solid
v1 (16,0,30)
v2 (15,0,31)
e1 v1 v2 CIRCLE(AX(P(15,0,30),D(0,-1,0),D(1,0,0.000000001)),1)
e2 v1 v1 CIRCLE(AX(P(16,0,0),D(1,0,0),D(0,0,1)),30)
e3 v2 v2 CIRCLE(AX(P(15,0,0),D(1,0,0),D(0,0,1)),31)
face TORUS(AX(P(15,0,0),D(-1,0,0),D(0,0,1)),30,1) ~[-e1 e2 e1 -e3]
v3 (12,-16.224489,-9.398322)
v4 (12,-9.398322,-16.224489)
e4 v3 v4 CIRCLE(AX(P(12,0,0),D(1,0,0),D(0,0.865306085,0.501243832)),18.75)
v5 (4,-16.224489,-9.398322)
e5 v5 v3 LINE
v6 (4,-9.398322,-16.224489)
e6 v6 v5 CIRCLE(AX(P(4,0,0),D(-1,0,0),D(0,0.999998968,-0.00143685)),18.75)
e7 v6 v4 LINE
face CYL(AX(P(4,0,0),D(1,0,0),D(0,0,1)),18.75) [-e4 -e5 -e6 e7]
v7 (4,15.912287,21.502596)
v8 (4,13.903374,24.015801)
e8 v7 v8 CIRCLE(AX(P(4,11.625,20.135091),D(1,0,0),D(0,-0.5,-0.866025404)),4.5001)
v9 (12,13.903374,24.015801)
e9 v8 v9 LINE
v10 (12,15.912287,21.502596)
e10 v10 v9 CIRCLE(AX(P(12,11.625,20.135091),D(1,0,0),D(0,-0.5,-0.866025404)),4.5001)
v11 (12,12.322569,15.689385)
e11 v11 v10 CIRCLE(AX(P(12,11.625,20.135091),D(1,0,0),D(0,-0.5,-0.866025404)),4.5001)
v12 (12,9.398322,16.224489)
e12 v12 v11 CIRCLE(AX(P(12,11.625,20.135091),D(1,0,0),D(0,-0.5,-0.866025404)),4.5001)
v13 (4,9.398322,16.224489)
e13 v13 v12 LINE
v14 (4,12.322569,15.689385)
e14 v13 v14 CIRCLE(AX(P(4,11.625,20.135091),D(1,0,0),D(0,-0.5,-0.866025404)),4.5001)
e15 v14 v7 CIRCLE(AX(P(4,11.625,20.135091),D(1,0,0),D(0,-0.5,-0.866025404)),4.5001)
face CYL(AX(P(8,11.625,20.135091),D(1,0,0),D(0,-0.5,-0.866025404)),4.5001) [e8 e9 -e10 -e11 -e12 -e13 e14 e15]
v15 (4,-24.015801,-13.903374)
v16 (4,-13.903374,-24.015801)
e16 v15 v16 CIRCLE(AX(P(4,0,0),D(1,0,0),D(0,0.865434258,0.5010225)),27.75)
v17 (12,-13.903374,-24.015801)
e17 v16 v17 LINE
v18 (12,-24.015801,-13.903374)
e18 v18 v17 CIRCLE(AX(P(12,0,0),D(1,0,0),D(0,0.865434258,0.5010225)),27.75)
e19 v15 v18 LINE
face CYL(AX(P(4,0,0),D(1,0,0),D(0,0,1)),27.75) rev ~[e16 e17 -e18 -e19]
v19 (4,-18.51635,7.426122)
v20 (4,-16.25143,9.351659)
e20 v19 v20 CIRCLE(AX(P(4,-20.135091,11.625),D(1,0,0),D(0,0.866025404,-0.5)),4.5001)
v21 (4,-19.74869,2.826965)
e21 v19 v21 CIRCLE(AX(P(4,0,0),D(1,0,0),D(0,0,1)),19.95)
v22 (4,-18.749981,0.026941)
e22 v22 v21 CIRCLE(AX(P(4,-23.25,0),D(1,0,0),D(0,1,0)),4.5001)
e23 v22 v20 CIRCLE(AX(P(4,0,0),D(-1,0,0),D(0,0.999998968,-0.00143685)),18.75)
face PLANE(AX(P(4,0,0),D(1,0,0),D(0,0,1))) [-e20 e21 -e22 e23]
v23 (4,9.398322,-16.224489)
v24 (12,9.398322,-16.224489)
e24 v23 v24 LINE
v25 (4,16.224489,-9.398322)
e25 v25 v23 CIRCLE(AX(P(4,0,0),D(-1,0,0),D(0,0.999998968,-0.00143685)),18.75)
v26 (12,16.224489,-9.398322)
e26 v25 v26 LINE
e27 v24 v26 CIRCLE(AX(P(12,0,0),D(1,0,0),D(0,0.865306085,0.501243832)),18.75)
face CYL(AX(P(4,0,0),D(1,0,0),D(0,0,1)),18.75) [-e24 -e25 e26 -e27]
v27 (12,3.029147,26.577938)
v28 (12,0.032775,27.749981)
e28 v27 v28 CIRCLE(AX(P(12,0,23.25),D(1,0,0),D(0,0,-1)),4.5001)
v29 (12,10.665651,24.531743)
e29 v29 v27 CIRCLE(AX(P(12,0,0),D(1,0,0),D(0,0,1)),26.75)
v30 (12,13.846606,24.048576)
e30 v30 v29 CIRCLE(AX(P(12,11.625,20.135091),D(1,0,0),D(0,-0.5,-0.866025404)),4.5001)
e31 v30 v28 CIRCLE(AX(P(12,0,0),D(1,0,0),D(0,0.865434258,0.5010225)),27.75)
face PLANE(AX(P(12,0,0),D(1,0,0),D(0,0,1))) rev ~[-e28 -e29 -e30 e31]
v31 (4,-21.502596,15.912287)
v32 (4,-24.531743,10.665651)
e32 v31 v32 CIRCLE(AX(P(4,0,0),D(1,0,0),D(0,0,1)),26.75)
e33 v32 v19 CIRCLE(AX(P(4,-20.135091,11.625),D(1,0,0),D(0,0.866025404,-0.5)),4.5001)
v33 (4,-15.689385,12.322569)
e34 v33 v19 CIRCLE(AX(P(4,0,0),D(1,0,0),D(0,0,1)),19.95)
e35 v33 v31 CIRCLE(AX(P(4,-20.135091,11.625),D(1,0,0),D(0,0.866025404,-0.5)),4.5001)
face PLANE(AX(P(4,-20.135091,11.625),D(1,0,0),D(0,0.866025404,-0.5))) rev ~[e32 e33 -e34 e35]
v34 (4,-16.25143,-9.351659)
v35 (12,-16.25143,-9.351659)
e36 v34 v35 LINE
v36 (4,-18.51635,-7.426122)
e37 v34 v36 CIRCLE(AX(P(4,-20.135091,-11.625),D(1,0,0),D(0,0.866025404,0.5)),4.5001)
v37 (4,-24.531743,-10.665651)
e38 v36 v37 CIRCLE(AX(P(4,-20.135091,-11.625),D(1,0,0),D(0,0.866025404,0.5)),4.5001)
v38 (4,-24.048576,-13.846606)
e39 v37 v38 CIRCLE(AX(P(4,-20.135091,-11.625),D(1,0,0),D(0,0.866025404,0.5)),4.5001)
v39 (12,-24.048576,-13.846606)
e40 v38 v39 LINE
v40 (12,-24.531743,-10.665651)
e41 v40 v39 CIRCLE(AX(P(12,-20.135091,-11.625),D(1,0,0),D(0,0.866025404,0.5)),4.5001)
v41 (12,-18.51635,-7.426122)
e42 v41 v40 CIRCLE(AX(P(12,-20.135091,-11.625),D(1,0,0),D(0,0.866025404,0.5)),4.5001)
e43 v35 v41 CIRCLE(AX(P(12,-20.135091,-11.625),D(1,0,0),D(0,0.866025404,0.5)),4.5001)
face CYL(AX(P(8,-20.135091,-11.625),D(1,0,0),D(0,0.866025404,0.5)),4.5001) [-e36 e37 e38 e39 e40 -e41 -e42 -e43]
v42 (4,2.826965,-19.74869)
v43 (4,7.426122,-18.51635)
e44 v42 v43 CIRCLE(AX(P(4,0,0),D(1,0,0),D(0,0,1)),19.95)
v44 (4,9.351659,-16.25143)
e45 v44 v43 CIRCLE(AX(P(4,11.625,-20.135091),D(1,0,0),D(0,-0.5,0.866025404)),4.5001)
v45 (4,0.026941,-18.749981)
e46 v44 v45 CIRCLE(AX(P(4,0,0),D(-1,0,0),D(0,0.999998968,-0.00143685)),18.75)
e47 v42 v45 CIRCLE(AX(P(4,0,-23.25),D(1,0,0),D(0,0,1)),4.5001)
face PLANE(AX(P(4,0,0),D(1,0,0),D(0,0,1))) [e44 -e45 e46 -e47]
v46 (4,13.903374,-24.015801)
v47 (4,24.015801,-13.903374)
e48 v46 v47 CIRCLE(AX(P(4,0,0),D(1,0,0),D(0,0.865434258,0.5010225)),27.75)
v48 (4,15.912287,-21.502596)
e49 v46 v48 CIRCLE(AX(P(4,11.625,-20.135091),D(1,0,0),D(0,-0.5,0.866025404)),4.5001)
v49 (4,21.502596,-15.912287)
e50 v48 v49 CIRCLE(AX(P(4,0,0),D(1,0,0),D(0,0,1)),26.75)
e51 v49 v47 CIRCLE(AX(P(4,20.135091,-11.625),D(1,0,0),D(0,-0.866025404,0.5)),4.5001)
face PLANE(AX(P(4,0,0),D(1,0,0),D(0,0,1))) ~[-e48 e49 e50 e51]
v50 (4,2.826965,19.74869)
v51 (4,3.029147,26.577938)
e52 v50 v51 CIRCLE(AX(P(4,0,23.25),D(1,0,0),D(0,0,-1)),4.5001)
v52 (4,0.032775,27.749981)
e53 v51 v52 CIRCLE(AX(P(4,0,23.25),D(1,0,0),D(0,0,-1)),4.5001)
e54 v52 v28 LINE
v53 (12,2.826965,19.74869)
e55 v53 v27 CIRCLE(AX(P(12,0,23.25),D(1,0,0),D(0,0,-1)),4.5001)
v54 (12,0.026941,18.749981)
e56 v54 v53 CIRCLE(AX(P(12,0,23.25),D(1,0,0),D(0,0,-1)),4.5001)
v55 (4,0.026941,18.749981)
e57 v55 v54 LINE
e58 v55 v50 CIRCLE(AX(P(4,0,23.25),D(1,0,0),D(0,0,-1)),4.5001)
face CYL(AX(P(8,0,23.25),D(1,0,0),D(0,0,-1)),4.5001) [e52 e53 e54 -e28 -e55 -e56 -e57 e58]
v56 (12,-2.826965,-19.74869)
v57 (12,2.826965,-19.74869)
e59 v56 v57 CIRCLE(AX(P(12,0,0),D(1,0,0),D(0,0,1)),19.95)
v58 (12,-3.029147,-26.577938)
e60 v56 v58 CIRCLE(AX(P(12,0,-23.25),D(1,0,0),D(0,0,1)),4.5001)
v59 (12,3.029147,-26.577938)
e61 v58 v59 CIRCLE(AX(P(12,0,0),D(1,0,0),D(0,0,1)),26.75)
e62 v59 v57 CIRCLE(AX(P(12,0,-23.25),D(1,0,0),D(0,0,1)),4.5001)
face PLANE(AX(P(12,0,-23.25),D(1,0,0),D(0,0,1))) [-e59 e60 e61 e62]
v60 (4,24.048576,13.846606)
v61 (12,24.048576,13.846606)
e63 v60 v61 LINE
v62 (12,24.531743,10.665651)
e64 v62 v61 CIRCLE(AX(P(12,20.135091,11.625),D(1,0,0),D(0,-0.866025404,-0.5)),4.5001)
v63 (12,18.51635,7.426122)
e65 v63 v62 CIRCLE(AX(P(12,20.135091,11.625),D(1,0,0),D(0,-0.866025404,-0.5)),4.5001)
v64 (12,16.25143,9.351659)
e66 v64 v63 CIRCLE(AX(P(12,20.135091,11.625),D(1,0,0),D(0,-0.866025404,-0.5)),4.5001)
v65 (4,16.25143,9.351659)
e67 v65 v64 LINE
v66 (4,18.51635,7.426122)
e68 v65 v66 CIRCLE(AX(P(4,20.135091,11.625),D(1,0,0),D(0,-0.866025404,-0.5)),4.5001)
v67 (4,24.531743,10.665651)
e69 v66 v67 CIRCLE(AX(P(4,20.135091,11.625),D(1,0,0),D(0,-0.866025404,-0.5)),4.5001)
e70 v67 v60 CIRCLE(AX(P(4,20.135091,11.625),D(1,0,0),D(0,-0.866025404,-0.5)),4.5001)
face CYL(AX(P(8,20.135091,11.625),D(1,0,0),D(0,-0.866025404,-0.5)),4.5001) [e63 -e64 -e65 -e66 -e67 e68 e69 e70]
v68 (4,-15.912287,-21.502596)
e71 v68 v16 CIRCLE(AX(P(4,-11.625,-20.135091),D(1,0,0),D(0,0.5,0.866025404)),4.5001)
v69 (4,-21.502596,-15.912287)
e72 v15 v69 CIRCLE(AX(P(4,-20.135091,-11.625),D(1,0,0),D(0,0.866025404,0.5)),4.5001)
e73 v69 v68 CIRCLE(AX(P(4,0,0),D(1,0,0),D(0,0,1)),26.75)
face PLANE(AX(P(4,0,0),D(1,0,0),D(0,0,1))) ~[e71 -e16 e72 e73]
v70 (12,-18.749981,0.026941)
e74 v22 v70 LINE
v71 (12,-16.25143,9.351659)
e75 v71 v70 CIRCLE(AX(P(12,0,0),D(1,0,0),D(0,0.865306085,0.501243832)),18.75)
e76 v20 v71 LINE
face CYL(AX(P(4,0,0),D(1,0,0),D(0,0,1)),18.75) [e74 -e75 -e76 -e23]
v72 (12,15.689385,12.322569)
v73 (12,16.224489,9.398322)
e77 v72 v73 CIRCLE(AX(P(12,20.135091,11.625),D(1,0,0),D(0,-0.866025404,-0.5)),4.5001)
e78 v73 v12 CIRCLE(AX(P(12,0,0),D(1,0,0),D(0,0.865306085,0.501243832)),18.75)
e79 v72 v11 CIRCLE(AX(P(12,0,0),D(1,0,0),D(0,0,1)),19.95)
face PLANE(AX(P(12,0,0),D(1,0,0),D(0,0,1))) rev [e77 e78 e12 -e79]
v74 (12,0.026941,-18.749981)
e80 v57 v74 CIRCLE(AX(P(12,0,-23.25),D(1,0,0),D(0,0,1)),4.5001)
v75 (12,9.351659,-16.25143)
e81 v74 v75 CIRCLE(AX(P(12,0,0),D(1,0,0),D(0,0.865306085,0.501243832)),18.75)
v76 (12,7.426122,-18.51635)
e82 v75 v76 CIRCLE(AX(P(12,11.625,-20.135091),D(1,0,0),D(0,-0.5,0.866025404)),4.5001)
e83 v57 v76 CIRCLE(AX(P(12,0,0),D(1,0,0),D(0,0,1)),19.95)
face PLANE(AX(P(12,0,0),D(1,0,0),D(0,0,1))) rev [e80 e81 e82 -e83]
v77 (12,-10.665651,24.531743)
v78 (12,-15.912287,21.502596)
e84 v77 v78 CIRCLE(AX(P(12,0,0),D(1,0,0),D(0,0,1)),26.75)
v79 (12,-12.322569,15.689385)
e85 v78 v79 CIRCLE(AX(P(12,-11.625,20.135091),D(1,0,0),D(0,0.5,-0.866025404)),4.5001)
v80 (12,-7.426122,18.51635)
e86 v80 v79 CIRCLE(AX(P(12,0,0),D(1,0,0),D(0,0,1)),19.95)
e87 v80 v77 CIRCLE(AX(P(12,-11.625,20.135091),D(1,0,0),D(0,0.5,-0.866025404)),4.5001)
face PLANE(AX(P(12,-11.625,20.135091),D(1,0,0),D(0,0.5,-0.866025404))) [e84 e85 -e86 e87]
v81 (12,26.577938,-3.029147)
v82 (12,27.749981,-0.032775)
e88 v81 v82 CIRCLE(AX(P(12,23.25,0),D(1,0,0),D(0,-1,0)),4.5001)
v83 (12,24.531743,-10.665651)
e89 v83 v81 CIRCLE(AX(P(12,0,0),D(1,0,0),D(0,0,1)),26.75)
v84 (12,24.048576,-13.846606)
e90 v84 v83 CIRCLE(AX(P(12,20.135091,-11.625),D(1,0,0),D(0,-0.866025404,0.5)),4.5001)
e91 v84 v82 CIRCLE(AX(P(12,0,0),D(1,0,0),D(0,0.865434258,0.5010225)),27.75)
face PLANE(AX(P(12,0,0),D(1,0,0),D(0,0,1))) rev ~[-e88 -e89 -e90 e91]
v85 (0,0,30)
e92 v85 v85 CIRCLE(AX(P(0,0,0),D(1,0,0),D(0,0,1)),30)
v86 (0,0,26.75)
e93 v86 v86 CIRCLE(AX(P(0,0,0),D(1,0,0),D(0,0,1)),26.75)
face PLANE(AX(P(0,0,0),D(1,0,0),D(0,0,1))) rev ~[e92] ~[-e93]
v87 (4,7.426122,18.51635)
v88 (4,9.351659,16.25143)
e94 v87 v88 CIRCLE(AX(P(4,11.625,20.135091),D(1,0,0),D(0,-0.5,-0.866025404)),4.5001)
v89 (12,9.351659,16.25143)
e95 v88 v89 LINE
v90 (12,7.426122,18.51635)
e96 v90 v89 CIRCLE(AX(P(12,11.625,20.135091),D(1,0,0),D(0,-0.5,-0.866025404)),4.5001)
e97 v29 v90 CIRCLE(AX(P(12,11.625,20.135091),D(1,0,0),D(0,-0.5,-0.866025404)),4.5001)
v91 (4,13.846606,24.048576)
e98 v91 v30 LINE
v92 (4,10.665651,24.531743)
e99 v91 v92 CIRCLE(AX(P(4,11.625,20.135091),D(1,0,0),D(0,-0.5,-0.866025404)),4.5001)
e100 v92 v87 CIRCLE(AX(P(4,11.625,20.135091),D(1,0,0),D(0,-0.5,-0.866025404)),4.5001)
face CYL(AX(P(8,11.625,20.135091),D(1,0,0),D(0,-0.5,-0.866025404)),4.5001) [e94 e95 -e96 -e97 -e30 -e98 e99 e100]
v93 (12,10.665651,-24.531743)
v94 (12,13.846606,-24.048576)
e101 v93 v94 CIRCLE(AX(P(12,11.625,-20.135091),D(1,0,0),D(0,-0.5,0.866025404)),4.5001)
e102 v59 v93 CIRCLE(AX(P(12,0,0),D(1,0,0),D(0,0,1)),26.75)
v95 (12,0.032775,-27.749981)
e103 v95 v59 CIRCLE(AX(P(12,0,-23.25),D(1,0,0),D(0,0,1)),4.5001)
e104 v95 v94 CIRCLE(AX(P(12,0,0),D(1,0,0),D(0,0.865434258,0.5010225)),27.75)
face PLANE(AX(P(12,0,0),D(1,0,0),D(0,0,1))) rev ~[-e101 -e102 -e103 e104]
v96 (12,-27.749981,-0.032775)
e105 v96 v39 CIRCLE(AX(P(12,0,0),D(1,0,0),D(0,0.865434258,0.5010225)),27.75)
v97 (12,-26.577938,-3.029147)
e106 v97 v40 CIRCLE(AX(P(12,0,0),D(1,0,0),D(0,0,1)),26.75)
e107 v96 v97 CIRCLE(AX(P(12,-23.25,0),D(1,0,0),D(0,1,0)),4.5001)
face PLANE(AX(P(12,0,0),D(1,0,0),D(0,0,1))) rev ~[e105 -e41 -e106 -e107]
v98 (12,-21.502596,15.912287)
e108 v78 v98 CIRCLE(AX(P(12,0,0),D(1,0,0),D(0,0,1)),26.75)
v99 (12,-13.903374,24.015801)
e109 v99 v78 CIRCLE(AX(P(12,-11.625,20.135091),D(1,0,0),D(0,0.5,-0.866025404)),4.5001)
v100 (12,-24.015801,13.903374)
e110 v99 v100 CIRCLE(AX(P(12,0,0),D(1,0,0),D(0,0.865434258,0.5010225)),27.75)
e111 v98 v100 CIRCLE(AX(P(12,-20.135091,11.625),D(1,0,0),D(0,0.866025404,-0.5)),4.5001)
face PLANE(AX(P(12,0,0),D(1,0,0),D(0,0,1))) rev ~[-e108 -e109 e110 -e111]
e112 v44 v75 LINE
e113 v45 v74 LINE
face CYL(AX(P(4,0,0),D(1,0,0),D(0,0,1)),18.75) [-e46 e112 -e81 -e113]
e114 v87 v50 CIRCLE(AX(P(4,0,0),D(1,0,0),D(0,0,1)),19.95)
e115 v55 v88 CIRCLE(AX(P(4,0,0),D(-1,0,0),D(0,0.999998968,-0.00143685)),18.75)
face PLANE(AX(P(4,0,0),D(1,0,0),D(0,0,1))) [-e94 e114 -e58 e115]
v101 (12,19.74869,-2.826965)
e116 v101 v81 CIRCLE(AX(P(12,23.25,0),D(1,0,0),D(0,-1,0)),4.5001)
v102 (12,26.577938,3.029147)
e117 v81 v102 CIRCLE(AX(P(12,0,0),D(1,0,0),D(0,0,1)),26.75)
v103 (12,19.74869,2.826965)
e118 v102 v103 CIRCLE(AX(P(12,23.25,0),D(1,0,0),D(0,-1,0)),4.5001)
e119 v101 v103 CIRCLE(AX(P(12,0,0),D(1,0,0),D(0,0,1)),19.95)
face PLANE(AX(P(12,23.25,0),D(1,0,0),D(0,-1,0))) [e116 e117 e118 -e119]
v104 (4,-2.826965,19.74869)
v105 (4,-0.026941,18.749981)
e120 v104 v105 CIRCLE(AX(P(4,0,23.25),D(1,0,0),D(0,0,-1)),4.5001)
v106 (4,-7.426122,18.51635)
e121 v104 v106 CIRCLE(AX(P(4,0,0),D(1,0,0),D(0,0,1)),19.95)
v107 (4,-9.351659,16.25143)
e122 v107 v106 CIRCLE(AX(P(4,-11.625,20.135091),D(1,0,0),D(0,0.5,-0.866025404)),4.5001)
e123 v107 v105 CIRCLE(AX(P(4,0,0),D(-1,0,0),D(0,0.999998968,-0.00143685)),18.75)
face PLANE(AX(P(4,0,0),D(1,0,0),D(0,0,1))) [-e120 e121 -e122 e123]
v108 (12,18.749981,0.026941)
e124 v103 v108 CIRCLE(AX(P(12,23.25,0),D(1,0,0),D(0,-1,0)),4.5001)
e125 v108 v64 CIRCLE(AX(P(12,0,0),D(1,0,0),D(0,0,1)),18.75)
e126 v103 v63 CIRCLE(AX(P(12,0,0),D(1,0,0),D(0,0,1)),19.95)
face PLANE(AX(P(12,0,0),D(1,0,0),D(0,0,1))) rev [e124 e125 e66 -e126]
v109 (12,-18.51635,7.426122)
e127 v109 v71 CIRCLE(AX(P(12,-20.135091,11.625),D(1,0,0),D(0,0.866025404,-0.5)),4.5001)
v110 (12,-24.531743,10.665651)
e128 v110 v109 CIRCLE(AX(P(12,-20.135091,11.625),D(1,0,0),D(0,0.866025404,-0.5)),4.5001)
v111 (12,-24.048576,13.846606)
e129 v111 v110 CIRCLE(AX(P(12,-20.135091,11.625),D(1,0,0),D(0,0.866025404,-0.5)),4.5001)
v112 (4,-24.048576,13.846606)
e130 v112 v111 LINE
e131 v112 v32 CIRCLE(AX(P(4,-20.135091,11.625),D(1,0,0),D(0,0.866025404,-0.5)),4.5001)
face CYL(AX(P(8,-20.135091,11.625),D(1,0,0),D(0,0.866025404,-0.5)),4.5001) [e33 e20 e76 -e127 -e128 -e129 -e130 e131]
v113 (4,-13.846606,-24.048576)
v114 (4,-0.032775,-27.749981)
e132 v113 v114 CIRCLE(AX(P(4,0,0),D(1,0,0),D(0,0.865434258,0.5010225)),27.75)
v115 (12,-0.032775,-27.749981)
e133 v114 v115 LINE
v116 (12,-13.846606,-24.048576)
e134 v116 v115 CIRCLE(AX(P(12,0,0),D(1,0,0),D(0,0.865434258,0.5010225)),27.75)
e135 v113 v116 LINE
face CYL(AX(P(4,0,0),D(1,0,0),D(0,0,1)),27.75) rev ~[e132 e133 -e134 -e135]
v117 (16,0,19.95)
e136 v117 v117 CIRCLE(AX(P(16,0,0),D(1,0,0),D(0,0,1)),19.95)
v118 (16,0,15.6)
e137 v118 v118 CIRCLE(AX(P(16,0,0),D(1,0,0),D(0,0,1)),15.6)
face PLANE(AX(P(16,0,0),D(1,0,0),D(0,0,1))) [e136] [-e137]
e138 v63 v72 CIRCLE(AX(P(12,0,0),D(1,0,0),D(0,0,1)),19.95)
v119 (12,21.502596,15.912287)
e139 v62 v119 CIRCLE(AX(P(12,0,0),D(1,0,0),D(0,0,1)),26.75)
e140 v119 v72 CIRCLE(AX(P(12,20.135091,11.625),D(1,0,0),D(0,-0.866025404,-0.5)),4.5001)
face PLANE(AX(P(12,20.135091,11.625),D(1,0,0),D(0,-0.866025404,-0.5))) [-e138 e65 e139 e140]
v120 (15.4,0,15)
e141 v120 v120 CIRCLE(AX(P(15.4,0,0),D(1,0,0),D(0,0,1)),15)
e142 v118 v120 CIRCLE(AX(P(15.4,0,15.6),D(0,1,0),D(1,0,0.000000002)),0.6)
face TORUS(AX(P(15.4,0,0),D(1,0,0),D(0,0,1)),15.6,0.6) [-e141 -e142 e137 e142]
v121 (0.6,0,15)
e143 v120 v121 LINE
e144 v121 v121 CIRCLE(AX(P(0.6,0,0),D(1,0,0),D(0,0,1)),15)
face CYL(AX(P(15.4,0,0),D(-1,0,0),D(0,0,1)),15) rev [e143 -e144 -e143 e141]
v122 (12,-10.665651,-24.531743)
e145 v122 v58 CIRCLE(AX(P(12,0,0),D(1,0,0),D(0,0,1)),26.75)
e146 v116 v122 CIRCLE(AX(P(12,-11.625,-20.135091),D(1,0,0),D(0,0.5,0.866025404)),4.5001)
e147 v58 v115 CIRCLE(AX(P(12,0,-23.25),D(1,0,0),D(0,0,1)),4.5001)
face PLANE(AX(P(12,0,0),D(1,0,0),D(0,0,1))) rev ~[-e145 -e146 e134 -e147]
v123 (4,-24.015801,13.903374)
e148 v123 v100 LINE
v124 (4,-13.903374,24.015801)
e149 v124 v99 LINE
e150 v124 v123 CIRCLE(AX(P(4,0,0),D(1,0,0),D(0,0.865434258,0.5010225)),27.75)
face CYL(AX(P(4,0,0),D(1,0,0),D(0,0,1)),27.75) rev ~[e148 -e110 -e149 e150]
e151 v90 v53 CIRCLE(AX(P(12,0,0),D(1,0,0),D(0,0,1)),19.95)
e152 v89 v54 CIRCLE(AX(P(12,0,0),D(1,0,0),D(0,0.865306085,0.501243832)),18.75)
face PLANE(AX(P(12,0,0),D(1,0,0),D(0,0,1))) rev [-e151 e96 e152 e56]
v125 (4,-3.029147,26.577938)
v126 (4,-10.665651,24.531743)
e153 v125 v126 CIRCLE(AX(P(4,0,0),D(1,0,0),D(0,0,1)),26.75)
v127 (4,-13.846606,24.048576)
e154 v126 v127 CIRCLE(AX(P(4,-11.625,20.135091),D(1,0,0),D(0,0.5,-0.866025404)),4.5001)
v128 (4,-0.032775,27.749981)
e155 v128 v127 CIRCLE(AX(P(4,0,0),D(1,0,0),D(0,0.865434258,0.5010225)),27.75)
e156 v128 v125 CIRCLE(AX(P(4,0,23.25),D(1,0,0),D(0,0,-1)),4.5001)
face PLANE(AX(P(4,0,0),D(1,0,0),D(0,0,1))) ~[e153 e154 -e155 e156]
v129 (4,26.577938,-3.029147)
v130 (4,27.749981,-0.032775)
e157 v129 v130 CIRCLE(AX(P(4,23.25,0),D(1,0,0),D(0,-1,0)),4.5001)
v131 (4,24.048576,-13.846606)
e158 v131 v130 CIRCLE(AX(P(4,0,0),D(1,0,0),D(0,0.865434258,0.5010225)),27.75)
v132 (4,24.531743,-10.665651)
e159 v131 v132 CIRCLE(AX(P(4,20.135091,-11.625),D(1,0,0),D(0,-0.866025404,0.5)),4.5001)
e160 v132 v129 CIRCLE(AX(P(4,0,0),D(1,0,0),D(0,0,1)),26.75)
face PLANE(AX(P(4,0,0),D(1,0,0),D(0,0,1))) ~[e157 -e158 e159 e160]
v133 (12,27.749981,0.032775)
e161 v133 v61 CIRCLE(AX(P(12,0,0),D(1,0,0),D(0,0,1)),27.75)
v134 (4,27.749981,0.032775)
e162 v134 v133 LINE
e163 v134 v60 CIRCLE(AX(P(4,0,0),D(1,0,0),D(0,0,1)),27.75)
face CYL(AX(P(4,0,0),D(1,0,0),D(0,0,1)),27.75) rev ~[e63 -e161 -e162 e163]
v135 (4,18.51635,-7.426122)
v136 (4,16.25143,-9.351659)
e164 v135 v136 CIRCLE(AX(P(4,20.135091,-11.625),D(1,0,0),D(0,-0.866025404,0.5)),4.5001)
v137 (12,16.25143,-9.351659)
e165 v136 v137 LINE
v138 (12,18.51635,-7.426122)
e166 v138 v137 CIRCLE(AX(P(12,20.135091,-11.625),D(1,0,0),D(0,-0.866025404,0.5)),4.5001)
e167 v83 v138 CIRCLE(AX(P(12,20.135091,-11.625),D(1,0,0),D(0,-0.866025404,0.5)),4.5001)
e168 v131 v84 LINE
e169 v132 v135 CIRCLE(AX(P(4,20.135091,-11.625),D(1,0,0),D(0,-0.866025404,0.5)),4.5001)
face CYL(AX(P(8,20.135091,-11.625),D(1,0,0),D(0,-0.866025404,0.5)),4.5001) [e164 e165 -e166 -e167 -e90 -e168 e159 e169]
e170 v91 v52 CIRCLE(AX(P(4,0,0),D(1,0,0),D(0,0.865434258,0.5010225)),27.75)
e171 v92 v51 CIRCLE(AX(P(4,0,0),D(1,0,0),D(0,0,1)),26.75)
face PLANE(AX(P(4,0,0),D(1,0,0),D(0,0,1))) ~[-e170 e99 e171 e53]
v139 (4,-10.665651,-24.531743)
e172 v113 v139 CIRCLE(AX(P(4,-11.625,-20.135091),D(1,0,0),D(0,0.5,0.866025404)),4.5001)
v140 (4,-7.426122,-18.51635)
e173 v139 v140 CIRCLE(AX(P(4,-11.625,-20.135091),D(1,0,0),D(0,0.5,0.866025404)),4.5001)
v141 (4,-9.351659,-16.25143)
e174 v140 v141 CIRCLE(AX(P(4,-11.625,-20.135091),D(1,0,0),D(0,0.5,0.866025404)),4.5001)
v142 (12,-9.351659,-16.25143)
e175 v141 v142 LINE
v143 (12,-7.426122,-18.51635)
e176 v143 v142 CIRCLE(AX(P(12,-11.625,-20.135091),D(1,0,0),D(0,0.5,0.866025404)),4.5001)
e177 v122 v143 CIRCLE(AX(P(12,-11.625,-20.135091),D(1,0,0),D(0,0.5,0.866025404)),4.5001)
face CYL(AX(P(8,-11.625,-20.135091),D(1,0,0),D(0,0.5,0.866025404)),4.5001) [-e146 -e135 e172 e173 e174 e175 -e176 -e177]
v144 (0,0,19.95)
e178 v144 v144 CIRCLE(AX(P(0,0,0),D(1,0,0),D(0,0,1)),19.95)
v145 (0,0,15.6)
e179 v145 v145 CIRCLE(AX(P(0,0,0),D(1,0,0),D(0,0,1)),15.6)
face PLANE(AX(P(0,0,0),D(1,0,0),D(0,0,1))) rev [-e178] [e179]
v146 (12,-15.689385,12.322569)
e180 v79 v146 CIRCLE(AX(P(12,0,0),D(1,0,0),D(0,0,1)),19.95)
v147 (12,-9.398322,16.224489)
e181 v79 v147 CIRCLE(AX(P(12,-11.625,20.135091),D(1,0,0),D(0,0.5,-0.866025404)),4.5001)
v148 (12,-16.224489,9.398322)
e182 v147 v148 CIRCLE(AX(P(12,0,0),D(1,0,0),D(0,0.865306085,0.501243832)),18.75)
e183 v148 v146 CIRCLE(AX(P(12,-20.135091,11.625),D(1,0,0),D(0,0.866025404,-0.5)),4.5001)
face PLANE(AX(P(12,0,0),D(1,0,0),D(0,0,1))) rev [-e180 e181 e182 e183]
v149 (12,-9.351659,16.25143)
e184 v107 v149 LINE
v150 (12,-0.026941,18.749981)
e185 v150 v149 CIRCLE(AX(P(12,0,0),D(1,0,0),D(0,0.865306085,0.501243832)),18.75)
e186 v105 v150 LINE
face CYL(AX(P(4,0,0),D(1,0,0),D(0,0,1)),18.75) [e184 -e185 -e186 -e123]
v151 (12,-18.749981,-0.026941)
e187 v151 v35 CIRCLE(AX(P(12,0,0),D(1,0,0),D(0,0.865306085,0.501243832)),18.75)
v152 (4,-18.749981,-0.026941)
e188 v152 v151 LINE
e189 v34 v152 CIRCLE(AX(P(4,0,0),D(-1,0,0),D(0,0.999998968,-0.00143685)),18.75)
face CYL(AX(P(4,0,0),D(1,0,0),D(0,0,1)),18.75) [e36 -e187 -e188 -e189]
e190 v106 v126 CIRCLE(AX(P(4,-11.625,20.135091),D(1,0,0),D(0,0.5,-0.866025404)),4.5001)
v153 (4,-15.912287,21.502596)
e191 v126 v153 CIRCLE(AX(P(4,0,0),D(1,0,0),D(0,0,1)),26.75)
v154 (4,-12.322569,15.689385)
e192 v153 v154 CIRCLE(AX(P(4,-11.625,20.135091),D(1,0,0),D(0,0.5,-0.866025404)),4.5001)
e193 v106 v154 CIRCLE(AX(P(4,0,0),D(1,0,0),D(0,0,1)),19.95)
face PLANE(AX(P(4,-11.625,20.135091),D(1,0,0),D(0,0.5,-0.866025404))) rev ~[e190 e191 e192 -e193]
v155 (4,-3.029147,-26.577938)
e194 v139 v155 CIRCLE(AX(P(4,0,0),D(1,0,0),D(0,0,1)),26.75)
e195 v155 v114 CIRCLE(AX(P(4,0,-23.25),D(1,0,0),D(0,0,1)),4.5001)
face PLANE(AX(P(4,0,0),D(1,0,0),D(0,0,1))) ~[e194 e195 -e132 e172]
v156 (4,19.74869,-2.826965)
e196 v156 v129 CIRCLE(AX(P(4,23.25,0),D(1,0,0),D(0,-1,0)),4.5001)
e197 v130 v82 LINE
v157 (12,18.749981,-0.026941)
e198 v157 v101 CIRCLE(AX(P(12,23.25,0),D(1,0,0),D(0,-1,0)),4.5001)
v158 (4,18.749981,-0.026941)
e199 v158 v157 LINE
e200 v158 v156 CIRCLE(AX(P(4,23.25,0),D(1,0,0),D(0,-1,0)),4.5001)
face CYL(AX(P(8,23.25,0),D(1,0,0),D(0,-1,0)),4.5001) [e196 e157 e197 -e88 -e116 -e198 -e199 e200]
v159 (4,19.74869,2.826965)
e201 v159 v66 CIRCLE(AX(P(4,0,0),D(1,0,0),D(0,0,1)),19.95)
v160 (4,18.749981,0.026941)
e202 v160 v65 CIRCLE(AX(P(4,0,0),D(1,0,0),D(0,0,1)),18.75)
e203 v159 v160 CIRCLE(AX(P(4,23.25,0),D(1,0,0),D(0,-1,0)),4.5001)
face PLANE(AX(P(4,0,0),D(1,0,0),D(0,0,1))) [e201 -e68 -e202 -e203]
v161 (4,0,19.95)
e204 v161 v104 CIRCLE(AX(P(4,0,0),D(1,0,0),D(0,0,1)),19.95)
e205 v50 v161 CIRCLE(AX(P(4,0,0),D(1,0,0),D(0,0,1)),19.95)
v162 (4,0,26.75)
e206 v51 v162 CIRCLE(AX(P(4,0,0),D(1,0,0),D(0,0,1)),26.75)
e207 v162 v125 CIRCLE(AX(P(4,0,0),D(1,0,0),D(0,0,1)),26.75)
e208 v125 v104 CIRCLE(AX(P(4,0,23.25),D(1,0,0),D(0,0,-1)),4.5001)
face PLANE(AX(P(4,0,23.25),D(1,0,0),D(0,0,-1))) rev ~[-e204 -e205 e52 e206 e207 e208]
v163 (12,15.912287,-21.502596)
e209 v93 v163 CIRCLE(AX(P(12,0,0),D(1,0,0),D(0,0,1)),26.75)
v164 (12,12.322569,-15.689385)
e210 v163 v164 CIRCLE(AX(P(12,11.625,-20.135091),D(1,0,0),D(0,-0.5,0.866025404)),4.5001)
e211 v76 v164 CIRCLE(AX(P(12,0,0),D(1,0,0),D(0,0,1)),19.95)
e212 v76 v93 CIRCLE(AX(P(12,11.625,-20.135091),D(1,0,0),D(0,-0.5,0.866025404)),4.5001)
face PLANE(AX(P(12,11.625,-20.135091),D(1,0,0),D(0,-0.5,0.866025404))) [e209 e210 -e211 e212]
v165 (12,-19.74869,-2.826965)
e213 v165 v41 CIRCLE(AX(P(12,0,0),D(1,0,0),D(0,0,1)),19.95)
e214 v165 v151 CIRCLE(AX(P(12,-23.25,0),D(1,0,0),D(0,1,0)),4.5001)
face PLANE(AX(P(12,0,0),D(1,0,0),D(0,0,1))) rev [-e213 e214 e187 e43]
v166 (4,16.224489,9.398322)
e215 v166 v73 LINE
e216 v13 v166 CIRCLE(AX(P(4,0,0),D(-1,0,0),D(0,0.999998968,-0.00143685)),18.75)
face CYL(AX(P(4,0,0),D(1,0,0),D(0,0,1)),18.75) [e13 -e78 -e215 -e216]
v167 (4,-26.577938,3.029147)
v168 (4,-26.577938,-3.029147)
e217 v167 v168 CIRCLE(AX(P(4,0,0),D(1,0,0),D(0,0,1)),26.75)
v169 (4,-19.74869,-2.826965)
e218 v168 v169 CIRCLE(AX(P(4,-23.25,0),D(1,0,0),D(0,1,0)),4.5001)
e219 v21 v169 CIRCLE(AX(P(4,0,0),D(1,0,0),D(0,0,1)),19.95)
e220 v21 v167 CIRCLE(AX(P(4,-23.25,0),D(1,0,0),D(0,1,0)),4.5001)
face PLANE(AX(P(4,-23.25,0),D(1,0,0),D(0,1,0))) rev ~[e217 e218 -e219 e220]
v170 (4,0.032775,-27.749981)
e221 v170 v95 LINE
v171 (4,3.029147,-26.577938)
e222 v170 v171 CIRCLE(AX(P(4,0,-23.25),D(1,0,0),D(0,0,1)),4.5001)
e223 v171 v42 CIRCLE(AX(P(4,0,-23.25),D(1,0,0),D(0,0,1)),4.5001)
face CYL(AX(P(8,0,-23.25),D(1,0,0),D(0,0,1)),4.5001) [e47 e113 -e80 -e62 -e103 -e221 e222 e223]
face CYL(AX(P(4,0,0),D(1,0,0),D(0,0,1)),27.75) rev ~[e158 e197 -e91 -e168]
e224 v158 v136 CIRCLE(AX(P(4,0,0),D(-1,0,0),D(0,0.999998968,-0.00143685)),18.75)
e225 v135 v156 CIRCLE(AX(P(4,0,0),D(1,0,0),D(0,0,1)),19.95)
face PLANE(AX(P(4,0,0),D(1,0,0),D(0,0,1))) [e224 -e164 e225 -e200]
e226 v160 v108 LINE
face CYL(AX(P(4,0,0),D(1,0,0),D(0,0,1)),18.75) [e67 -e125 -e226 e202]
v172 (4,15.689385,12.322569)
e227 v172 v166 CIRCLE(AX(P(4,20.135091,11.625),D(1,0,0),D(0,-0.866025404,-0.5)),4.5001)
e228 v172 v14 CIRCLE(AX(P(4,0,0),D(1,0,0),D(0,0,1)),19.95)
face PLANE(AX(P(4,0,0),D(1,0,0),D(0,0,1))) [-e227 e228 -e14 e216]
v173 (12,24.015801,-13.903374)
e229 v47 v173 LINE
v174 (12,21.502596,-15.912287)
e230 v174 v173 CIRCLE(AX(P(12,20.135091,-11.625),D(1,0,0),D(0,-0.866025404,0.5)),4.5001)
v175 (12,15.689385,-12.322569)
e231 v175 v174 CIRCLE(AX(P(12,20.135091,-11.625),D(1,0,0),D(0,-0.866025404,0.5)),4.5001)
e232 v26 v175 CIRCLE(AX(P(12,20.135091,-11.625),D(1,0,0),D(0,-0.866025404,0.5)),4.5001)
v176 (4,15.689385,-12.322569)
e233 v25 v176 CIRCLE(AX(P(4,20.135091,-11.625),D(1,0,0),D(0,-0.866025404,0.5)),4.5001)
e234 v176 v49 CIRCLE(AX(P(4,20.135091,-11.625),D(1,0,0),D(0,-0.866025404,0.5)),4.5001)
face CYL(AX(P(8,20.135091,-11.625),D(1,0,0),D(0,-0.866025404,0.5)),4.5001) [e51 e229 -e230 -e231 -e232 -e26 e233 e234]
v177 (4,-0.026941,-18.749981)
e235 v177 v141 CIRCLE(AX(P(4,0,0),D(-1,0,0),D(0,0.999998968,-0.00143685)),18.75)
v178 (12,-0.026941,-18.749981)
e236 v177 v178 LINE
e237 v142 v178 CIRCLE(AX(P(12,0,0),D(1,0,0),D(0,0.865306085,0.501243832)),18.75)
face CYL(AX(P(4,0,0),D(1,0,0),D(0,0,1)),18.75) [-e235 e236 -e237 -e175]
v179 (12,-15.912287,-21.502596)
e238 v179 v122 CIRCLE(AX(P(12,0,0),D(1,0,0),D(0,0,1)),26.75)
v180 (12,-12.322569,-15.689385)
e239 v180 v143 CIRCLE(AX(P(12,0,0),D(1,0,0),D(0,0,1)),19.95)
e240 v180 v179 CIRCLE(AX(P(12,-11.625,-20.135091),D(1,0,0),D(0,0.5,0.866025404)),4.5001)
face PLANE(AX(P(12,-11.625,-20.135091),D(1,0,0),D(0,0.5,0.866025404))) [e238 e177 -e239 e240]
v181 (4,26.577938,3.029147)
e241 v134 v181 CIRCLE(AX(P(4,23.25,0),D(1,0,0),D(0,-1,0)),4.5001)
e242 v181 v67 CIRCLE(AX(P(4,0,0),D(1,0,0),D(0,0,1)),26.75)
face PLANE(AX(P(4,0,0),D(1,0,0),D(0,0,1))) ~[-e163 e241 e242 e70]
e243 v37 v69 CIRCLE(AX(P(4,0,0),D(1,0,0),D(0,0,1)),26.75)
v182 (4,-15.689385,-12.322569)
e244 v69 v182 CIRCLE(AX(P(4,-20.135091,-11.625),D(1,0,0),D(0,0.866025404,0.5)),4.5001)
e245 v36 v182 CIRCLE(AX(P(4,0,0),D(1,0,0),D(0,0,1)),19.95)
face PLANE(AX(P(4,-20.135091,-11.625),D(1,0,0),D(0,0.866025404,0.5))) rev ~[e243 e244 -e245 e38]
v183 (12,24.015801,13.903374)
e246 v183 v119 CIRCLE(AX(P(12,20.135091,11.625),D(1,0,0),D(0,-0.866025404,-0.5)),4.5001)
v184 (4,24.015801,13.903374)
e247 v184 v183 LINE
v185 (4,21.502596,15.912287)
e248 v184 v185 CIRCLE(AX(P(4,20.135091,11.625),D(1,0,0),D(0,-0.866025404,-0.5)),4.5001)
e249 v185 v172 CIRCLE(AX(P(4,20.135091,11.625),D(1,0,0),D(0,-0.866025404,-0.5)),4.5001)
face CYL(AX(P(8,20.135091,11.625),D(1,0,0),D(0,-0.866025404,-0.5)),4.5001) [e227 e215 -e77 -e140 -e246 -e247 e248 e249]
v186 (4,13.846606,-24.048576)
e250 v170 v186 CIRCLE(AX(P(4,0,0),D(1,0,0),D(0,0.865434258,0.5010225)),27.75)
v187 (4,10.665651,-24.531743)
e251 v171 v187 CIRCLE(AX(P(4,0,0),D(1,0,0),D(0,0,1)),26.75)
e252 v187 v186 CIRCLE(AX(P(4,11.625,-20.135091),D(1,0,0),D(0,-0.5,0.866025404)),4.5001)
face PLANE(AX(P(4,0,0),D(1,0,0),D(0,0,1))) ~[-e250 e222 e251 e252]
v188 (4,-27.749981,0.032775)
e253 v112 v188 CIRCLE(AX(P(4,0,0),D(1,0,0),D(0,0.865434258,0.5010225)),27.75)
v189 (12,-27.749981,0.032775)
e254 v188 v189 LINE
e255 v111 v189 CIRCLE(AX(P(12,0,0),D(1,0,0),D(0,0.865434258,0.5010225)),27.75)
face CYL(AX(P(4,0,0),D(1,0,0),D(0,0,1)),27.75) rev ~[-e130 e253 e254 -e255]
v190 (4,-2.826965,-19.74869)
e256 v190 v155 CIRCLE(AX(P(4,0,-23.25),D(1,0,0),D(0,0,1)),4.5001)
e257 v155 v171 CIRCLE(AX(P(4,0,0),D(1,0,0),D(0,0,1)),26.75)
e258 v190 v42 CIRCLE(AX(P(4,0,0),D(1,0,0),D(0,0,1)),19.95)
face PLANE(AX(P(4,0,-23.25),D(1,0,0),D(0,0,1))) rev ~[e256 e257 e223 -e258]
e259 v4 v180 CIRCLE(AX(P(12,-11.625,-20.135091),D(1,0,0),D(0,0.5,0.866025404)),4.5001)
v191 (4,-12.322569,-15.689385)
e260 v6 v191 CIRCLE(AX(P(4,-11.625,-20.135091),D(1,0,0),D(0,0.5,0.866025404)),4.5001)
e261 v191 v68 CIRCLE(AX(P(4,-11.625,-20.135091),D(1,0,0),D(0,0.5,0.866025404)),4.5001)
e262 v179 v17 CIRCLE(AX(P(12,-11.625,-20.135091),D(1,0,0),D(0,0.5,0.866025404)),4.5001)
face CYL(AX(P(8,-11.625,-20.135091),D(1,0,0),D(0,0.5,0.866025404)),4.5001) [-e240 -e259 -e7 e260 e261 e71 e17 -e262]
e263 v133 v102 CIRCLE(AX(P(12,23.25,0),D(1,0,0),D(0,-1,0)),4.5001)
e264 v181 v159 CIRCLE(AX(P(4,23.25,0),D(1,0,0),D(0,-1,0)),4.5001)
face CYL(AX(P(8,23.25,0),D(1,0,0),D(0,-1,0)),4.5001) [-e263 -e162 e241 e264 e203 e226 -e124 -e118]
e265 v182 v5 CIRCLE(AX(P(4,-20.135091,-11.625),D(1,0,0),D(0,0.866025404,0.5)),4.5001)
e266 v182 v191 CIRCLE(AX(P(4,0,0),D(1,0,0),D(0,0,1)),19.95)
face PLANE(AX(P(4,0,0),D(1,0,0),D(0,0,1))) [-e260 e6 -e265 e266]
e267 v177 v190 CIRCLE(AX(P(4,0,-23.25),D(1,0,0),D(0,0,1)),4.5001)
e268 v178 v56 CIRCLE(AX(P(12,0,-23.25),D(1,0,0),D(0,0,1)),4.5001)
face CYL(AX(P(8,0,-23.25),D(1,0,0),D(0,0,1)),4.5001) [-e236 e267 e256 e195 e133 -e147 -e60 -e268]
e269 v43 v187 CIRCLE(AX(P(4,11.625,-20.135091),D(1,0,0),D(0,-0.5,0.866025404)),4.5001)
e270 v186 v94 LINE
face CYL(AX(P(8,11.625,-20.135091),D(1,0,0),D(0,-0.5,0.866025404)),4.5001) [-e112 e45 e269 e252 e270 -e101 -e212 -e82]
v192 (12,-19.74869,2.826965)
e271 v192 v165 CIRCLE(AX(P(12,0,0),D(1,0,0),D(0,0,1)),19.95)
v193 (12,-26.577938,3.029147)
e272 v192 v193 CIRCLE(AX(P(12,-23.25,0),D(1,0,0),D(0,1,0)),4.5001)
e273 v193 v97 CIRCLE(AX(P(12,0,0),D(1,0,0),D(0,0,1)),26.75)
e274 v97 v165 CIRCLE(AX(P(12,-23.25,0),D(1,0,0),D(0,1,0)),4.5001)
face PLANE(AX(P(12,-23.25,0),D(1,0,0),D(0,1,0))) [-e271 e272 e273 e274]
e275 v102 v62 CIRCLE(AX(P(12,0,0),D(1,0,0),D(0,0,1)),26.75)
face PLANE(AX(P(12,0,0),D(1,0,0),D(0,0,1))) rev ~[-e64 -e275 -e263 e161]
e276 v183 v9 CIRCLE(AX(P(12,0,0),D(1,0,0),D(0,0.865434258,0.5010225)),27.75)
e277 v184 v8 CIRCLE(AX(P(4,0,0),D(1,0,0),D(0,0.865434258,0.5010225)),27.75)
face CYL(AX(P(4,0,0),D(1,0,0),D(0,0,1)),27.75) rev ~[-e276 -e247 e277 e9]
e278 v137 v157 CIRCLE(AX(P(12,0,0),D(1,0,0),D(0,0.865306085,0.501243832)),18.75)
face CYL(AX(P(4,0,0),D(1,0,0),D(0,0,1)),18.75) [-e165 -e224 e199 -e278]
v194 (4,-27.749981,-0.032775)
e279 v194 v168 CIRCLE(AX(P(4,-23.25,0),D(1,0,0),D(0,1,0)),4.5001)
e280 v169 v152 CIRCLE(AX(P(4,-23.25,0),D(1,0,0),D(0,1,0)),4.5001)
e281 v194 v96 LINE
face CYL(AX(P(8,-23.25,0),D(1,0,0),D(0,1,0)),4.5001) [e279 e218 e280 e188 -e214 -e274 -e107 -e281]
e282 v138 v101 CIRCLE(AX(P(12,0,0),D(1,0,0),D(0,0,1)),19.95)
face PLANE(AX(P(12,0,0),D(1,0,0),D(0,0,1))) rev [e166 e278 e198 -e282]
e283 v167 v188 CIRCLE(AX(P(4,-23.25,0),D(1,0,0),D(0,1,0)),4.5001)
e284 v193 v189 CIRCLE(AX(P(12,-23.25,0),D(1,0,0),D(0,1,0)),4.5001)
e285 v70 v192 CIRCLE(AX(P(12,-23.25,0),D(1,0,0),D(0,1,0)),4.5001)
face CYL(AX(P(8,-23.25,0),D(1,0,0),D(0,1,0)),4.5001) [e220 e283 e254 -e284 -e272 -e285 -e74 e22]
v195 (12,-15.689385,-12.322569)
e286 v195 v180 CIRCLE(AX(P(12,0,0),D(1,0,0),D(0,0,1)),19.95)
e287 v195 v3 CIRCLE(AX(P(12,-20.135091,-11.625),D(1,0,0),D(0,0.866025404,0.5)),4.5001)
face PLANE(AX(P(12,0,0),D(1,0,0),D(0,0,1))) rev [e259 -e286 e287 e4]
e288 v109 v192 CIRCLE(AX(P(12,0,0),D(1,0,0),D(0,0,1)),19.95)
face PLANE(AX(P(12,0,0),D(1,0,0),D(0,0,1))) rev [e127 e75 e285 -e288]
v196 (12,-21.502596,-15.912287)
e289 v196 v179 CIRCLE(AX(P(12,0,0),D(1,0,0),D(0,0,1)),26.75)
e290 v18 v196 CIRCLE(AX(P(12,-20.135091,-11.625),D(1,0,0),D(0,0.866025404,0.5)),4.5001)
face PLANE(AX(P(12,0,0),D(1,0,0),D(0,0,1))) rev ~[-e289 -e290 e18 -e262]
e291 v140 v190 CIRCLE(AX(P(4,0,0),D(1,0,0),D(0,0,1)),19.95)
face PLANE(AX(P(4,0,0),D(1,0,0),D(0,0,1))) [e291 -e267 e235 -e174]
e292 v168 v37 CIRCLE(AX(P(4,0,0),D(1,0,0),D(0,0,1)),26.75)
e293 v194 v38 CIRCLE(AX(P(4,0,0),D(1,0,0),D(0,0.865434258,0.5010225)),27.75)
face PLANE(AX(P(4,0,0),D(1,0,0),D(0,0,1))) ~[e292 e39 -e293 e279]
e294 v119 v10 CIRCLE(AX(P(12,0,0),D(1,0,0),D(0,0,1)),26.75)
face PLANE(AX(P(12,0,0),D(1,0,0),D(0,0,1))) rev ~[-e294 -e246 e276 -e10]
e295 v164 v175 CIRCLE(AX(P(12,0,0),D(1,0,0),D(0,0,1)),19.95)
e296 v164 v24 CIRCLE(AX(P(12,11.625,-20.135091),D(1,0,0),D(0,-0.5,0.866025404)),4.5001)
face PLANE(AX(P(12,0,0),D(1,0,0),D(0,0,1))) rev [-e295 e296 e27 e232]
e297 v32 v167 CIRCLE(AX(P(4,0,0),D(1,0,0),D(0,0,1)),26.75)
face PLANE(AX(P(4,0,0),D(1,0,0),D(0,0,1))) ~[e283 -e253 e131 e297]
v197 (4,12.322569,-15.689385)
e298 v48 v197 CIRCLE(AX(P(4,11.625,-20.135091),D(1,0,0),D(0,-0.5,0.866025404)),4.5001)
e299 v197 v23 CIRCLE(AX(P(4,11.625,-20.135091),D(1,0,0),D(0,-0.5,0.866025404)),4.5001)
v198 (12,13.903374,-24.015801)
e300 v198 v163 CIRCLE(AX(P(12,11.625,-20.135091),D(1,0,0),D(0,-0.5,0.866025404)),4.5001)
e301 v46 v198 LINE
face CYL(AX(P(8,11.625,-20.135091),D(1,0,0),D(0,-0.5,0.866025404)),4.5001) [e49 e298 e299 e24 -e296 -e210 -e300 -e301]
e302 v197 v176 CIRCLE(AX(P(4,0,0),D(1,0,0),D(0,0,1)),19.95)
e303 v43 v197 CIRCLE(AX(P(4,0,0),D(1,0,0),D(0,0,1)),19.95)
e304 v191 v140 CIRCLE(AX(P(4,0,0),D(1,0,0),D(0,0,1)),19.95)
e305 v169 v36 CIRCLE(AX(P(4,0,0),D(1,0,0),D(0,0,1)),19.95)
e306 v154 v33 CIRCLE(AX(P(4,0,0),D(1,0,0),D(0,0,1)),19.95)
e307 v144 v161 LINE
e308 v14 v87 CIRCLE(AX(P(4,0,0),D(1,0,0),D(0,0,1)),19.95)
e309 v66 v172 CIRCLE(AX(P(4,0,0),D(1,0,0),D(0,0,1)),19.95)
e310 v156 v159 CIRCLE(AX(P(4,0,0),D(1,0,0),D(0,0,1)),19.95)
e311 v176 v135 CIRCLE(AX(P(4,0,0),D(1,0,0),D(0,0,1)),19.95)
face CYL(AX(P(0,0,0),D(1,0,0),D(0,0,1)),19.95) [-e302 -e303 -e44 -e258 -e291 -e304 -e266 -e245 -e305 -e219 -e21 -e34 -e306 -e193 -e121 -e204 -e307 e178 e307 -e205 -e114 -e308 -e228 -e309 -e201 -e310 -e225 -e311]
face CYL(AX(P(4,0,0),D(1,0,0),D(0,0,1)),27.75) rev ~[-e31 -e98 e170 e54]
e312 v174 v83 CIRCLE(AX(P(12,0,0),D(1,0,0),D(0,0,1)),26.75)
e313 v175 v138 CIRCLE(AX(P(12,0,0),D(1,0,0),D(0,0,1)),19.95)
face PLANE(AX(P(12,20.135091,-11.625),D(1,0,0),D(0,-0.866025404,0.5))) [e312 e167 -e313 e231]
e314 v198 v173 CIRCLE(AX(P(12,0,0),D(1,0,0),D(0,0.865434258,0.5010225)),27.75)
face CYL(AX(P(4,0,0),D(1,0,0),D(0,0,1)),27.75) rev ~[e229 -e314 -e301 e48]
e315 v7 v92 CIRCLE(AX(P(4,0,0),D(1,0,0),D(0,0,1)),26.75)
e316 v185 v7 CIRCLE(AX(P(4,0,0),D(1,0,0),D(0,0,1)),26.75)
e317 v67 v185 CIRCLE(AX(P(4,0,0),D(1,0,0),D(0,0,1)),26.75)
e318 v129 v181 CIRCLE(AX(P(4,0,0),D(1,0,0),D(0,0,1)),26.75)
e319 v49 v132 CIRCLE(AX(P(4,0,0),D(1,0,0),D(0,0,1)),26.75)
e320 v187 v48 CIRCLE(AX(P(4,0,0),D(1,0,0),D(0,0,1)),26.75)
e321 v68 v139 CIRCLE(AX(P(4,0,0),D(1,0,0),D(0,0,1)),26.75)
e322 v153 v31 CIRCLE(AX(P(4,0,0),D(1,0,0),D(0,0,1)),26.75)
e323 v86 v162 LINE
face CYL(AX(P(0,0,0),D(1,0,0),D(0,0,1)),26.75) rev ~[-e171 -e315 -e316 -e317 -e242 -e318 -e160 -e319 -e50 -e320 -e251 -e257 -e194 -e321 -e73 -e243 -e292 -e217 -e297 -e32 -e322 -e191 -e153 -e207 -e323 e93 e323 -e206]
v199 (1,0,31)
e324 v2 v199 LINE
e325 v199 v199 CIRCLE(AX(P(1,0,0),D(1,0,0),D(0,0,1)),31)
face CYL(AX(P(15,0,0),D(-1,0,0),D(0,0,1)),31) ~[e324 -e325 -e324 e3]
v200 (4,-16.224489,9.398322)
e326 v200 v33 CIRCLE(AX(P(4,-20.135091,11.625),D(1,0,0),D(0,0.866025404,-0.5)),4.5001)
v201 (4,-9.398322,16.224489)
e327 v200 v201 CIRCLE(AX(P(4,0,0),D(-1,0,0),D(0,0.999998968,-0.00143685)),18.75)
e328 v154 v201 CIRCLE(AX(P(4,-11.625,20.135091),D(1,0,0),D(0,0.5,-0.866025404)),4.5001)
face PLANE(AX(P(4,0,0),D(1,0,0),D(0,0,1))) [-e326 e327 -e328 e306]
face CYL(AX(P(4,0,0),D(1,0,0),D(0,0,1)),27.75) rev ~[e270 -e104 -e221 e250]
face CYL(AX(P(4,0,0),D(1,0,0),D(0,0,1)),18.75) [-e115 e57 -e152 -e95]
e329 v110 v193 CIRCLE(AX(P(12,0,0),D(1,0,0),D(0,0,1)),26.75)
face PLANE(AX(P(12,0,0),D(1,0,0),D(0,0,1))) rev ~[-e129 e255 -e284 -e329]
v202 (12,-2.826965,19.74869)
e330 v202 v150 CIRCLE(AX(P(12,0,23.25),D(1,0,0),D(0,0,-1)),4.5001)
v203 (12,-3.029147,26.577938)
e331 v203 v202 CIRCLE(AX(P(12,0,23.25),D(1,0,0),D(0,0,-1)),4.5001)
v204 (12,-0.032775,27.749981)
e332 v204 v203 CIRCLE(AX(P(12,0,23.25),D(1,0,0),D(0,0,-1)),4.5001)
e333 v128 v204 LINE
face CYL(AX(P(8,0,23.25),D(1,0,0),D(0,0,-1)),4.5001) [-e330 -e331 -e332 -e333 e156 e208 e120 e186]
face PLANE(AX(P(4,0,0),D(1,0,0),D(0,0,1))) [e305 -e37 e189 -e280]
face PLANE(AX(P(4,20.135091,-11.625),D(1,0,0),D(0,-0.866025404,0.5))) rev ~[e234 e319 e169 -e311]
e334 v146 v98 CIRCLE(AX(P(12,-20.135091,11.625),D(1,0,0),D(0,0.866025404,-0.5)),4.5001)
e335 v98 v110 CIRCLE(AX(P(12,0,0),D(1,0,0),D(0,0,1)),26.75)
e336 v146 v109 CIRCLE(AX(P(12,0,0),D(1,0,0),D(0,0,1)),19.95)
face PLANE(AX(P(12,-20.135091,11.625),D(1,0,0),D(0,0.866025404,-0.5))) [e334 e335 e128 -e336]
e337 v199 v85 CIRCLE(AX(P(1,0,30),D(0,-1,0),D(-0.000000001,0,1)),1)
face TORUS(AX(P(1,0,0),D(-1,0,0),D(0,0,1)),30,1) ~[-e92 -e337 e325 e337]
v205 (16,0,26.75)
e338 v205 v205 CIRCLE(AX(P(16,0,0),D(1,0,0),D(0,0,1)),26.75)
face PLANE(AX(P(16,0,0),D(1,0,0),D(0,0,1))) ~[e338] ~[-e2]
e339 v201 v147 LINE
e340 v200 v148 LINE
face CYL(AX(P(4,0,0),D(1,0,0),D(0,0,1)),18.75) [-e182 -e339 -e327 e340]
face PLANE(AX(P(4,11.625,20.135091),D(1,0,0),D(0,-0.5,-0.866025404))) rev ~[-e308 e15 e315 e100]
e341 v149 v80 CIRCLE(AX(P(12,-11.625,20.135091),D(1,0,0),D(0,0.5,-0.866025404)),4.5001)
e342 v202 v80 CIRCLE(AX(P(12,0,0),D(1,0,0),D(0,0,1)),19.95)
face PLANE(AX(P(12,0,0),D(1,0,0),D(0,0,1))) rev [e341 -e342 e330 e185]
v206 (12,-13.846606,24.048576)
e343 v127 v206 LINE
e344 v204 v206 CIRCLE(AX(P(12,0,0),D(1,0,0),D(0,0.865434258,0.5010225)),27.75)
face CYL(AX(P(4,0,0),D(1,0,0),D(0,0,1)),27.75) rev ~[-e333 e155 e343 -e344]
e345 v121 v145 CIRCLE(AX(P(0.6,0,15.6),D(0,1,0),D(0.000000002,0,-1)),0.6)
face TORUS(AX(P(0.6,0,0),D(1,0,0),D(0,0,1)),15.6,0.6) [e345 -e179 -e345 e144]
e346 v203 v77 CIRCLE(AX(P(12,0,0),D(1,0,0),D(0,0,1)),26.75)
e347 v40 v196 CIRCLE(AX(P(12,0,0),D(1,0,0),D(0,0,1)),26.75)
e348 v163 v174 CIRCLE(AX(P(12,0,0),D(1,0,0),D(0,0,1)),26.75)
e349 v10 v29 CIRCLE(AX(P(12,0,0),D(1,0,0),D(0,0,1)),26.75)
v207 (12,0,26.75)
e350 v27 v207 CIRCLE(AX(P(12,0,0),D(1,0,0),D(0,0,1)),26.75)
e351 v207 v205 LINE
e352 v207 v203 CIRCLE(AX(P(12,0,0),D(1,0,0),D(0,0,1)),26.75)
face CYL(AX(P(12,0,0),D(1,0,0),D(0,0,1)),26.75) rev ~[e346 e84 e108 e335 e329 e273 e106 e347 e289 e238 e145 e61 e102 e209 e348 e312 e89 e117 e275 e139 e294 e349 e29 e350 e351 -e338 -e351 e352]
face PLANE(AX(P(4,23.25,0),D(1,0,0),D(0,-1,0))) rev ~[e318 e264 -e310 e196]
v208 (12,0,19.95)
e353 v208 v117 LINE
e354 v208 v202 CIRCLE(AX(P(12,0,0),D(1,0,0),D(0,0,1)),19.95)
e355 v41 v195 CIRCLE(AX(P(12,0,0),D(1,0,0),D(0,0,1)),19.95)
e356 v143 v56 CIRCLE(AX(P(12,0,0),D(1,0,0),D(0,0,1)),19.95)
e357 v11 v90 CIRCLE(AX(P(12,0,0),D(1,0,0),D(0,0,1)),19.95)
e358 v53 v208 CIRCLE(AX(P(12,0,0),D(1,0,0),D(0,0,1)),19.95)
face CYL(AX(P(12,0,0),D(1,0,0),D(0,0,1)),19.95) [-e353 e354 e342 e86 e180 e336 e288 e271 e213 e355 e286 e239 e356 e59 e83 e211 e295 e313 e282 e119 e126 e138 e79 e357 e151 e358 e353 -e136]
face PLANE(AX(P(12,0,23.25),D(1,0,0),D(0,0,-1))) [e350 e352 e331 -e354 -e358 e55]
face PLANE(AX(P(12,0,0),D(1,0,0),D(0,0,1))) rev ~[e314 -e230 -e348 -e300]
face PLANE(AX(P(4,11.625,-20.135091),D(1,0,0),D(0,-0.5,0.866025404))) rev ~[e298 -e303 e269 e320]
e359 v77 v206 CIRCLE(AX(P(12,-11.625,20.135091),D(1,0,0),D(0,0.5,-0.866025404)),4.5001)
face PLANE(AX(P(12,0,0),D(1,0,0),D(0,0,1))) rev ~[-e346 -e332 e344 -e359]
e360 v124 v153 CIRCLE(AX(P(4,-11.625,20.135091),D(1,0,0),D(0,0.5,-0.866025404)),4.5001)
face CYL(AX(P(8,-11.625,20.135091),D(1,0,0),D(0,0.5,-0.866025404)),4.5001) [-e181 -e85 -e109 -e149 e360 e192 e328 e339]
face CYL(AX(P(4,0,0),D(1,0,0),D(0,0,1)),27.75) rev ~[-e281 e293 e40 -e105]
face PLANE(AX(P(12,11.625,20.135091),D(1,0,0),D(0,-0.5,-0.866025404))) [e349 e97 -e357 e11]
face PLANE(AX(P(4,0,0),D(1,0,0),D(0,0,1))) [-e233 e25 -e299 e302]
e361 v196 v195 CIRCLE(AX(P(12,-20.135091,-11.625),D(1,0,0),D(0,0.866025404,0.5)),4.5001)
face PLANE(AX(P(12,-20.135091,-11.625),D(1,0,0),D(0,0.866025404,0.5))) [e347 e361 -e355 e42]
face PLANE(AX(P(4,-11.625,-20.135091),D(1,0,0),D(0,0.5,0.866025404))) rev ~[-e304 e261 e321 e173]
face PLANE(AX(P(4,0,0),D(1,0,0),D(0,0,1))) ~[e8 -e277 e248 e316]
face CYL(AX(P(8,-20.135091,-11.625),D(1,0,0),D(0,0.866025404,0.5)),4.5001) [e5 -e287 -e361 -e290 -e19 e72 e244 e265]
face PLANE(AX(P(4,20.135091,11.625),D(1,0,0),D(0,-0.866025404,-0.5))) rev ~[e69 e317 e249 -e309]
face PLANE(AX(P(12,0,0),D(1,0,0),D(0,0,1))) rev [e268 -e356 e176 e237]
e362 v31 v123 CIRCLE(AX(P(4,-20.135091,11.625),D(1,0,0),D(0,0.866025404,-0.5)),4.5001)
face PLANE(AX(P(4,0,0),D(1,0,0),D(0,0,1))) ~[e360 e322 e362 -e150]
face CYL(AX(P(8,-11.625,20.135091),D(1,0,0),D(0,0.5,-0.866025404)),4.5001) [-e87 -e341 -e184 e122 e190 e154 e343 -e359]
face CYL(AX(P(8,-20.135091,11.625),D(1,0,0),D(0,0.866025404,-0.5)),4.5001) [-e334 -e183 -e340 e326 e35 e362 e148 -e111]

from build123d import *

# Parameters (mm, degrees)
SKETCH_3_W               = 8
SKETCH_3_H               = 4.5001
PATTERN_CIRCULAR_1_COUNT = 12


with BuildPart() as part:
    # 草图2 → Revolve 705 (revolve)
    with BuildSketch(Plane.XY, mode=Mode.PRIVATE) as revolve_705_sk:
        with BuildLine():
            Line((4, 18.75), (12, 18.75))
            Line((12, 18.75), (12, 19.95))
            Line((12, 19.95), (16, 19.95))
            Line((16, 19.95), (16, 15.6))
            ThreePointArc((16, 15.6), (15.824264069, 15.175735931), (15.4, 15))
            Line((15.4, 15), (0.6, 15))
            ThreePointArc((0.6, 15), (0.175735931, 15.175735931), (0, 15.6))
            Line((0, 15.6), (0, 19.95))
            Line((0, 19.95), (4, 19.95))
            Line((4, 19.95), (4, 18.75))
        make_face()
    revolve(revolve_705_sk.sketch.rotate(Axis((-10.080094127, 0, 0), (1, 0, 0)), 90), axis=Axis((-10.080094127, 0, 0), (1, 0, 0)))

    # 草图3 → 凸台-旋转1 (revolve)
    with BuildSketch(Plane.XY):
        with Locations((8, 20.99995)):
            Rectangle(SKETCH_3_W, SKETCH_3_H)
    revolve_1 = revolve(axis=Axis((-1.603948851, 23.25, 0), (1, 0, 0)))

    # 草图4 → 凸台-旋转2 (revolve)
    with BuildSketch(Plane.XY, mode=Mode.PRIVATE) as revolve_2_sk:
        with BuildLine():
            Line((12, 26.75), (16, 26.75))
            Line((16, 26.75), (16, 30))
            ThreePointArc((16, 30), (15.707106781, 30.707106781), (15, 31))
            Line((15, 31), (1, 31))
            ThreePointArc((1, 31), (0.292893219, 30.707106781), (0, 30))
            Line((0, 30), (0, 26.75))
            Line((0, 26.75), (4, 26.75))
            Line((4, 26.75), (4, 27.75))
            Line((4, 27.75), (12, 27.75))
            Line((12, 27.75), (12, 26.75))
        make_face()
    revolve(revolve_2_sk.sketch.rotate(Axis((0, 0, 0), (1, 0, 0)), 90), axis=Axis((0, 0, 0), (1, 0, 0)))

    # 阵列(圆周)1: 凸台-旋转1 ×12 about axis
    pattern_circular_1_axis = Axis((0, 0, 0), (1, 0, 0))
    for i in range(1, PATTERN_CIRCULAR_1_COUNT):
        add(revolve_1.rotate(pattern_circular_1_axis, i * 360 / PATTERN_CIRCULAR_1_COUNT))


solid = part.part
